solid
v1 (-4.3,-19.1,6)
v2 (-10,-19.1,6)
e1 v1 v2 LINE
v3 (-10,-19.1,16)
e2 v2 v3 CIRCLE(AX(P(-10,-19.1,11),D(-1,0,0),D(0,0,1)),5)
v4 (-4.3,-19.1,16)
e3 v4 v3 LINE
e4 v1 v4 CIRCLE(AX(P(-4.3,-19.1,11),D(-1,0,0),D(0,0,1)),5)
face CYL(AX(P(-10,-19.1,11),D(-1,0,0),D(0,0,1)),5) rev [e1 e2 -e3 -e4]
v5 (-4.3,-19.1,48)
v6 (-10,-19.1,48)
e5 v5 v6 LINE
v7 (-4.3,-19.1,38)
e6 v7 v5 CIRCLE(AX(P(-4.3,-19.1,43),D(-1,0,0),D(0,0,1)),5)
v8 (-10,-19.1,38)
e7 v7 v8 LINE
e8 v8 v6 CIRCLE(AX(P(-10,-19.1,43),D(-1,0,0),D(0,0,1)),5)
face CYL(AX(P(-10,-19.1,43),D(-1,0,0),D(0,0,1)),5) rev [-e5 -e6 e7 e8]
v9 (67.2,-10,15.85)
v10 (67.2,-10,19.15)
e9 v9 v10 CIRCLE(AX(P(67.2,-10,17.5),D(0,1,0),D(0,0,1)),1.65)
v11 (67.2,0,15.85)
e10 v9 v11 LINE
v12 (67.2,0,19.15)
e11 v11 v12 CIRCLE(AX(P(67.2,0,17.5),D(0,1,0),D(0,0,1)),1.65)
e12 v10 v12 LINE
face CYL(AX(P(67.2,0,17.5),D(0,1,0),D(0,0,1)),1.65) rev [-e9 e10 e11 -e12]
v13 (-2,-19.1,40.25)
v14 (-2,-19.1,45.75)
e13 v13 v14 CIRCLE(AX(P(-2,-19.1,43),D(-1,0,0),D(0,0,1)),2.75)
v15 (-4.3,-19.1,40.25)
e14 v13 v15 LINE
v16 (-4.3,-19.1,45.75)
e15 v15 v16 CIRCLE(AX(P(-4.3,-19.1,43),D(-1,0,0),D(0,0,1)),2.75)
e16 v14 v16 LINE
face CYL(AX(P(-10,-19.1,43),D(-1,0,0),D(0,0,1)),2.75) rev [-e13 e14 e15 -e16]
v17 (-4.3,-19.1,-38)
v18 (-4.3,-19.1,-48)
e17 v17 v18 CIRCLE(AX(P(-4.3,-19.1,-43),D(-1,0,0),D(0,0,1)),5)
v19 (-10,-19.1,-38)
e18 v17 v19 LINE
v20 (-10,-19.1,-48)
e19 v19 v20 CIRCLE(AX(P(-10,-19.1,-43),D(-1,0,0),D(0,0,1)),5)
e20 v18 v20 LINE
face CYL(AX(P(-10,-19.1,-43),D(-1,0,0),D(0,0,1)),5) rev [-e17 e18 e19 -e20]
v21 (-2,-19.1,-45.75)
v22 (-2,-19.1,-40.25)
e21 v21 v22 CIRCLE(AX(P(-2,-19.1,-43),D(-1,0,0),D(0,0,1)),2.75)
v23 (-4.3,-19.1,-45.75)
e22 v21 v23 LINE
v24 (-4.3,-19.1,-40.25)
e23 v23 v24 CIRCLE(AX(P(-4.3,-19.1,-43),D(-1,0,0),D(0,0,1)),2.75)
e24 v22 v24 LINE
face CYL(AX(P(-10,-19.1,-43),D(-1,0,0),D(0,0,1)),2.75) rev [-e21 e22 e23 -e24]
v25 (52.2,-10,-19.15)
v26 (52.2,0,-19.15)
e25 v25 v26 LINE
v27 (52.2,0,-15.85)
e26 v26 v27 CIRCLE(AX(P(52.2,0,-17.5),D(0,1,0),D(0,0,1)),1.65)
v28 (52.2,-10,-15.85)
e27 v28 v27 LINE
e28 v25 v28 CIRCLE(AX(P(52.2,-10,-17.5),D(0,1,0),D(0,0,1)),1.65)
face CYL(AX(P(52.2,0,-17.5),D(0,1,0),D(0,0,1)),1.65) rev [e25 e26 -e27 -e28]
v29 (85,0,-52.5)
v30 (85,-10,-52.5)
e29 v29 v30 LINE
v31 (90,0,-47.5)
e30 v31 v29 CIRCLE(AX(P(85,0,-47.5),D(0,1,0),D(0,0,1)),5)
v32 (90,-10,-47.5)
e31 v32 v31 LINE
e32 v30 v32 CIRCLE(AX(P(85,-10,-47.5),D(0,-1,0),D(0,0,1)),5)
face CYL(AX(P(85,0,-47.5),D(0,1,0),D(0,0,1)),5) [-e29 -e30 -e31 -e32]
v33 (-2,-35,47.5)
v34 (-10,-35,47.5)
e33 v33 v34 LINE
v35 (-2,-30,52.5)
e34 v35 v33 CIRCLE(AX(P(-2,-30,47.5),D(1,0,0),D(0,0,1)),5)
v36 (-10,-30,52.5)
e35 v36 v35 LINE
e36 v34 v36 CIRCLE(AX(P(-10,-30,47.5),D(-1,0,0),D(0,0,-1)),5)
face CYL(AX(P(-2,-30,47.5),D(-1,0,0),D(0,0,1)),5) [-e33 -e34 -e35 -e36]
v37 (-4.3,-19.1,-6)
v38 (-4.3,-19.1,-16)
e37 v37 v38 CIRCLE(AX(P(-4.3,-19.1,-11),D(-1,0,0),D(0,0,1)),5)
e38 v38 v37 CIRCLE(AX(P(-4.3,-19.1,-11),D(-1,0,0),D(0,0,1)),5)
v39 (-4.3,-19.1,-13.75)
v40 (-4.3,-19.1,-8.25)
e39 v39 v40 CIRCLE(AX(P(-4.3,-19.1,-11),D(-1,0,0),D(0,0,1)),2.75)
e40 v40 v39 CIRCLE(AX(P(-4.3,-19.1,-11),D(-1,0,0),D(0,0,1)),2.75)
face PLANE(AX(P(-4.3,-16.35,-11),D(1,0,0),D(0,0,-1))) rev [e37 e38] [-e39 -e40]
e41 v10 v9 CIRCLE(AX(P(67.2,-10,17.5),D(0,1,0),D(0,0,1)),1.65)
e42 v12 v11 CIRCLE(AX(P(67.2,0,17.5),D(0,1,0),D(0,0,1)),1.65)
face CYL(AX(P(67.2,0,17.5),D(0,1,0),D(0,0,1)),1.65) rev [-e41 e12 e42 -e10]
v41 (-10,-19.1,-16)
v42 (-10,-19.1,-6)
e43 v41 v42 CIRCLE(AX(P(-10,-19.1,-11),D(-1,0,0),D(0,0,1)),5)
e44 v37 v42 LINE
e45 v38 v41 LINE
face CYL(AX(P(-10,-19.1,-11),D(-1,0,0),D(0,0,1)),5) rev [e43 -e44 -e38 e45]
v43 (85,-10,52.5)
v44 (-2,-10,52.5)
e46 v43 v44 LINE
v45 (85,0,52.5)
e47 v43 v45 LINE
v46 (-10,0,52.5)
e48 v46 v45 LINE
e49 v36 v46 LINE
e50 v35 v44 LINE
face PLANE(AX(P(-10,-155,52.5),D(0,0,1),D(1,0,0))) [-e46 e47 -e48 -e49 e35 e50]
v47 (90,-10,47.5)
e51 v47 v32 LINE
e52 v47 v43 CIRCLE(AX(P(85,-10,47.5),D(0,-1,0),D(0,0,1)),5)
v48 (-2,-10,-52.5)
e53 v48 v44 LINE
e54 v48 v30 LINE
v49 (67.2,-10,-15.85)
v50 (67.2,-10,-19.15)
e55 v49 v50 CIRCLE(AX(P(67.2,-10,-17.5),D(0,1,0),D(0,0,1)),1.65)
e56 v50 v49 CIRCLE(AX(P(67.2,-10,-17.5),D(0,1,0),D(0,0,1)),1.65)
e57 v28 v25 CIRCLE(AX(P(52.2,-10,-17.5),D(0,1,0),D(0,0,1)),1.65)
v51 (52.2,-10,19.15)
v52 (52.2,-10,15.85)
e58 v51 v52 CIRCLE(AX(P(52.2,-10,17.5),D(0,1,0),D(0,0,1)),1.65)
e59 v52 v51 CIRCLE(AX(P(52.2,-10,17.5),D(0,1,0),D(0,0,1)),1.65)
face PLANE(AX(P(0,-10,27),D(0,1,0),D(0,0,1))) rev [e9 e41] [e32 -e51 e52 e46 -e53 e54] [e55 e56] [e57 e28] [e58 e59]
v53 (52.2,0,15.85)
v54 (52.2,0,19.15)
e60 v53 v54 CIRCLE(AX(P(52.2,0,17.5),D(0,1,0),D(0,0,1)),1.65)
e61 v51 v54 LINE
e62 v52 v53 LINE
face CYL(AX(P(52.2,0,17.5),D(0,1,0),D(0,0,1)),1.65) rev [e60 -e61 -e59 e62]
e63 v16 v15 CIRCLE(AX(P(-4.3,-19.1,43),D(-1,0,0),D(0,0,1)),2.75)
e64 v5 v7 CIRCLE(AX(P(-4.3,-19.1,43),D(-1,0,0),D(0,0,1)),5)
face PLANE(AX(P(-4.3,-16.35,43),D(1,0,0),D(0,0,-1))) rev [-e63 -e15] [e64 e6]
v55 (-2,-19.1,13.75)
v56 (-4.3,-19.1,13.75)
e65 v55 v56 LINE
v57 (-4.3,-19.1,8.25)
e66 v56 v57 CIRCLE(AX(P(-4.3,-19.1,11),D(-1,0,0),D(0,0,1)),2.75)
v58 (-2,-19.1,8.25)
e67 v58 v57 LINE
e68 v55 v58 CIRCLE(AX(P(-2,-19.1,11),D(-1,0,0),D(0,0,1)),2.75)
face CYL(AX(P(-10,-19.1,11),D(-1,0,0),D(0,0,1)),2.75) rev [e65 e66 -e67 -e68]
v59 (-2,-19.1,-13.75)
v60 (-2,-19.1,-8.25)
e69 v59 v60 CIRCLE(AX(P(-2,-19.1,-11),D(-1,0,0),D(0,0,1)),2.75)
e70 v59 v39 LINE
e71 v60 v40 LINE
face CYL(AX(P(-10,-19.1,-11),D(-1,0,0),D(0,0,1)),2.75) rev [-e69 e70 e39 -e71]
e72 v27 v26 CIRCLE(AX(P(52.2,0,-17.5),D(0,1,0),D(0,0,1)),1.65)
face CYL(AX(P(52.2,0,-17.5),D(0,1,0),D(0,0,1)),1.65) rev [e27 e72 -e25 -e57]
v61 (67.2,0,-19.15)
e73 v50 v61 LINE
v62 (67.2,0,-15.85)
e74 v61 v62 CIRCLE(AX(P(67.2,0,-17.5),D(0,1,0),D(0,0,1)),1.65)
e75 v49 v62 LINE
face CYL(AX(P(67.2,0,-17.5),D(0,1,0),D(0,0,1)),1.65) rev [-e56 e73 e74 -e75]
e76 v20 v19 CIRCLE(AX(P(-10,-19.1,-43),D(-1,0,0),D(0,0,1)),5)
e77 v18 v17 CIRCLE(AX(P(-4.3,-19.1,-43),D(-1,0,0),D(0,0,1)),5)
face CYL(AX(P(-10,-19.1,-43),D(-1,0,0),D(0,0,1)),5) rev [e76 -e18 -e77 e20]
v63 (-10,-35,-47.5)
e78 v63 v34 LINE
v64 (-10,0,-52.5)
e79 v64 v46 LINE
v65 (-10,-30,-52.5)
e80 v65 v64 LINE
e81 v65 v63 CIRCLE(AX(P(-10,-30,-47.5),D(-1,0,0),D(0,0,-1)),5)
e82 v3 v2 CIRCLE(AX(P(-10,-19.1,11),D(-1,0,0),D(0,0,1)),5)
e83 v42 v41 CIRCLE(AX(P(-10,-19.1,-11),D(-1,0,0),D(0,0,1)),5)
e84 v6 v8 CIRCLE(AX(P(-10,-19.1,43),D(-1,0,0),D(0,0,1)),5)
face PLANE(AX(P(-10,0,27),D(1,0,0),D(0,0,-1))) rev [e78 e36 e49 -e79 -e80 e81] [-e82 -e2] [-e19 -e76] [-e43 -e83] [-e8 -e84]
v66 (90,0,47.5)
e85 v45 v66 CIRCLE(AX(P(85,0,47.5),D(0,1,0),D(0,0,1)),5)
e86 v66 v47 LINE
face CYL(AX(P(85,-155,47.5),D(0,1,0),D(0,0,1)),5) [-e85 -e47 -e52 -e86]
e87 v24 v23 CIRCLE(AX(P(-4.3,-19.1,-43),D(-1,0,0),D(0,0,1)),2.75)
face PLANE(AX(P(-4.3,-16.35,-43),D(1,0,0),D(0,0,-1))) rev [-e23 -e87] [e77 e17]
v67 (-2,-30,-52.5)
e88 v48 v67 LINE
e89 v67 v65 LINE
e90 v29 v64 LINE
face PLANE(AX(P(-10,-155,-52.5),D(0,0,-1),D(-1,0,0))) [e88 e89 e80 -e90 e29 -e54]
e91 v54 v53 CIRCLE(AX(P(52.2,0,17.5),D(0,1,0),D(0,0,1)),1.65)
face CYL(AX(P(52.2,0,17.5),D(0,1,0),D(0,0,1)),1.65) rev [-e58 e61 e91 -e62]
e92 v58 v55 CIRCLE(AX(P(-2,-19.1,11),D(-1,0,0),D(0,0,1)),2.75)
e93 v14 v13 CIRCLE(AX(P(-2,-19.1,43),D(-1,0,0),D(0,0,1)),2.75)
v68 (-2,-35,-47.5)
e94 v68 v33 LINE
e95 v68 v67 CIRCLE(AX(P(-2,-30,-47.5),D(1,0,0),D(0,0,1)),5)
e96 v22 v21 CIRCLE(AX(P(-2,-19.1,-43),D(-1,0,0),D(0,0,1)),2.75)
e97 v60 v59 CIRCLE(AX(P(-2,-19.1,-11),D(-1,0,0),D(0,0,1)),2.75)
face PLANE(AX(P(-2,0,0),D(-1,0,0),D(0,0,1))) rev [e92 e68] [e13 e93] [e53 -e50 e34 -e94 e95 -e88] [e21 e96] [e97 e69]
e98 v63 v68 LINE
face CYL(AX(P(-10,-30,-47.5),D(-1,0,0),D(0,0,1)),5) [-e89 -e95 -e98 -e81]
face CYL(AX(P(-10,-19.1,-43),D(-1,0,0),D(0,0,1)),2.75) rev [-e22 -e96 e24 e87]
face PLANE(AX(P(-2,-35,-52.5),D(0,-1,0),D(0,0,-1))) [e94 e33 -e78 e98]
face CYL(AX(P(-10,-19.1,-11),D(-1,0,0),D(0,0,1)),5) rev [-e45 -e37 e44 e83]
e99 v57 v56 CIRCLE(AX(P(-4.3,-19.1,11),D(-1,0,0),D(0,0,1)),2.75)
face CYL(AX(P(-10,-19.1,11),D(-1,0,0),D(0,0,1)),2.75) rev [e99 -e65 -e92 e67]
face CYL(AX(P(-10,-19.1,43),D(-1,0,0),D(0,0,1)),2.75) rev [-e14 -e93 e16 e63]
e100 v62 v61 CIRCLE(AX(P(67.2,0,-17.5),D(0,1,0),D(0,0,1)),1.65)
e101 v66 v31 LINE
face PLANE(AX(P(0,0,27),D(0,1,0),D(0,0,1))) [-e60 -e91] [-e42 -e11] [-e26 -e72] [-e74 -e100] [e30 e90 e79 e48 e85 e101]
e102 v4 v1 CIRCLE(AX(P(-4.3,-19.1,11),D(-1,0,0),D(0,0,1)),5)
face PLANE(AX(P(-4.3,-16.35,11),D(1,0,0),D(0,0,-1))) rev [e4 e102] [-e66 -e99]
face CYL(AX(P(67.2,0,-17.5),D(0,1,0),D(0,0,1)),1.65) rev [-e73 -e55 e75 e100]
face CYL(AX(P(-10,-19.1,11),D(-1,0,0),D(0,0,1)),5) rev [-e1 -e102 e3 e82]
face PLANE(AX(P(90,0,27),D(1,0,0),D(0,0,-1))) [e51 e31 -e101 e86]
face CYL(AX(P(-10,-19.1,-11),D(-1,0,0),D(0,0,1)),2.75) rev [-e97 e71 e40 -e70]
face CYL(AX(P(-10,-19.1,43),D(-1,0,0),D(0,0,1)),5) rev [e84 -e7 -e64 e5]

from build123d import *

# Parameters (mm, degrees)
EXTRUDE_1_DEPTH              = 27
SKETCH_2_R                   = 16
CUT_EXTRUDE_1_DEPTH          = 107.437775249
EXTRUDE_START                = -1.2
SKETCH_3_R                   = 16
SKETCH_3_R_2                 = 15
EXTRUDE_1_2_DEPTH            = 1.2
SKETCH_5_W                   = 100
SKETCH_5_H                   = 105
EXTRUDE_2_DEPTH              = 10
FILLET_1_R                   = 5
HOLE_WIZARD_M4_1_D           = 3.3
SKETCH_10_W                  = 21.869488537
SKETCH_10_H                  = 58.553791887
CUT_EXTRUDE_2_DEPTH          = 50
SKETCH_11_W                  = 105
SKETCH_11_H                  = 35
EXTRUDE_3_DEPTH              = 8
HOLE_WIZARD_M5_1_D           = 5.5
HOLE_WIZARD_M5_1_DEPTH       = 10.1
HOLE_WIZARD_M5_1_CBORE_D     = 10
HOLE_WIZARD_M5_1_CBORE_DEPTH = 5.7
HOLE_WIZARD_M5_1_TIP         = 1.652366702
FILLET_2_R                   = 5


with BuildPart() as part:
    # 草图1 → Extrude 1 (new, symmetric)
    with BuildSketch(Plane.XY):
        Polygon((90, 0), (0, 0), (0, 50), (-10, 50), (-10, -10), (90, -10), align=None)
    extrude(amount=EXTRUDE_1_DEPTH, both=True)

    # 草图2 → 切除-拉伸1 (cut, through all)
    with BuildSketch(Plane(origin=(0, 0, 0), x_dir=(0, 0, -1), z_dir=(1, 0, 0))):
        with Locations((0, 30)):
            Circle(SKETCH_2_R)
    extrude(amount=-CUT_EXTRUDE_1_DEPTH, mode=Mode.SUBTRACT)

    # 草图3 → Extrude 1 2 (add)
    with BuildSketch(Plane.ZY.offset(10).offset(EXTRUDE_START)):
        with Locations(Location((0, 30, 0), (0, 0, 180))):
            Circle(SKETCH_3_R)
        with Locations((0, 30)):
            Circle(SKETCH_3_R_2, mode=Mode.SUBTRACT)
    extrude(amount=EXTRUDE_1_2_DEPTH)

    # 草图5 → 凸台-拉伸2 (add)
    with BuildSketch(Plane(origin=(0, 0, 0), x_dir=(1, 0, 0), z_dir=(0, 1, 0))):
        with Locations((40, 0)):
            Rectangle(SKETCH_5_W, SKETCH_5_H)
    extrude(amount=-EXTRUDE_2_DEPTH)

    # 圆角1
    fillet_1_edges = [part.edges().sort_by_distance(p)[0] for p in [
        (-5, 50, 27),
        (90, -5, -52.5),
        (90, -5, 52.5),
        (-5, 50, -27),
    ]]
    fillet(fillet_1_edges, radius=FILLET_1_R)

    # M4 螺纹孔1 (through all)
    with Locations(Plane(origin=(67.2, 0, 17.5), x_dir=(0, 0, 1), z_dir=(0, 1, 0))):
        with Locations((0, 0), (0, -15), (-35, 0), (-35, -15)):
            Hole(HOLE_WIZARD_M4_1_D / 2)

    # 草图10 → 切除-拉伸2 (cut)
    with BuildSketch(Plane(origin=(0, 50, 0), x_dir=(1, 0, 0), z_dir=(0, 1, 0))):
        with Locations((-5.309523809, -0.493827161)):
            Rectangle(SKETCH_10_W, SKETCH_10_H)
    extrude(amount=-CUT_EXTRUDE_2_DEPTH, mode=Mode.SUBTRACT)

    # 草图11 → 凸台-拉伸3 (add)
    with BuildSketch(Plane.ZY.offset(10)):
        with Locations((0, -17.5)):
            Rectangle(SKETCH_11_W, SKETCH_11_H)
    extrude(amount=-EXTRUDE_3_DEPTH)

    # M5 六角圆柱头螺钉的柱形沉头孔1
    with Locations(Plane(origin=(-10, -19.1, -43), x_dir=(0, 0, -1), z_dir=(-1, 0, 0))):
        with Locations((0, 0), (-32, 0), (-54, 0), (-86, 0)):
            CounterBoreHole(HOLE_WIZARD_M5_1_D / 2, HOLE_WIZARD_M5_1_CBORE_D / 2, HOLE_WIZARD_M5_1_CBORE_DEPTH, depth=HOLE_WIZARD_M5_1_DEPTH)
            with Locations((0, 0, -(HOLE_WIZARD_M5_1_DEPTH + HOLE_WIZARD_M5_1_TIP / 2))):  # 118° drill point
                Cone(0, HOLE_WIZARD_M5_1_D / 2, HOLE_WIZARD_M5_1_TIP, mode=Mode.SUBTRACT)

    # 圆角2
    fillet_2_edges = [part.edges().sort_by_distance(p)[0] for p in [
        (-6, -35, -52.5),
        (-6, -35, 52.5),
    ]]
    fillet(fillet_2_edges, radius=FILLET_2_R)


solid = part.part
